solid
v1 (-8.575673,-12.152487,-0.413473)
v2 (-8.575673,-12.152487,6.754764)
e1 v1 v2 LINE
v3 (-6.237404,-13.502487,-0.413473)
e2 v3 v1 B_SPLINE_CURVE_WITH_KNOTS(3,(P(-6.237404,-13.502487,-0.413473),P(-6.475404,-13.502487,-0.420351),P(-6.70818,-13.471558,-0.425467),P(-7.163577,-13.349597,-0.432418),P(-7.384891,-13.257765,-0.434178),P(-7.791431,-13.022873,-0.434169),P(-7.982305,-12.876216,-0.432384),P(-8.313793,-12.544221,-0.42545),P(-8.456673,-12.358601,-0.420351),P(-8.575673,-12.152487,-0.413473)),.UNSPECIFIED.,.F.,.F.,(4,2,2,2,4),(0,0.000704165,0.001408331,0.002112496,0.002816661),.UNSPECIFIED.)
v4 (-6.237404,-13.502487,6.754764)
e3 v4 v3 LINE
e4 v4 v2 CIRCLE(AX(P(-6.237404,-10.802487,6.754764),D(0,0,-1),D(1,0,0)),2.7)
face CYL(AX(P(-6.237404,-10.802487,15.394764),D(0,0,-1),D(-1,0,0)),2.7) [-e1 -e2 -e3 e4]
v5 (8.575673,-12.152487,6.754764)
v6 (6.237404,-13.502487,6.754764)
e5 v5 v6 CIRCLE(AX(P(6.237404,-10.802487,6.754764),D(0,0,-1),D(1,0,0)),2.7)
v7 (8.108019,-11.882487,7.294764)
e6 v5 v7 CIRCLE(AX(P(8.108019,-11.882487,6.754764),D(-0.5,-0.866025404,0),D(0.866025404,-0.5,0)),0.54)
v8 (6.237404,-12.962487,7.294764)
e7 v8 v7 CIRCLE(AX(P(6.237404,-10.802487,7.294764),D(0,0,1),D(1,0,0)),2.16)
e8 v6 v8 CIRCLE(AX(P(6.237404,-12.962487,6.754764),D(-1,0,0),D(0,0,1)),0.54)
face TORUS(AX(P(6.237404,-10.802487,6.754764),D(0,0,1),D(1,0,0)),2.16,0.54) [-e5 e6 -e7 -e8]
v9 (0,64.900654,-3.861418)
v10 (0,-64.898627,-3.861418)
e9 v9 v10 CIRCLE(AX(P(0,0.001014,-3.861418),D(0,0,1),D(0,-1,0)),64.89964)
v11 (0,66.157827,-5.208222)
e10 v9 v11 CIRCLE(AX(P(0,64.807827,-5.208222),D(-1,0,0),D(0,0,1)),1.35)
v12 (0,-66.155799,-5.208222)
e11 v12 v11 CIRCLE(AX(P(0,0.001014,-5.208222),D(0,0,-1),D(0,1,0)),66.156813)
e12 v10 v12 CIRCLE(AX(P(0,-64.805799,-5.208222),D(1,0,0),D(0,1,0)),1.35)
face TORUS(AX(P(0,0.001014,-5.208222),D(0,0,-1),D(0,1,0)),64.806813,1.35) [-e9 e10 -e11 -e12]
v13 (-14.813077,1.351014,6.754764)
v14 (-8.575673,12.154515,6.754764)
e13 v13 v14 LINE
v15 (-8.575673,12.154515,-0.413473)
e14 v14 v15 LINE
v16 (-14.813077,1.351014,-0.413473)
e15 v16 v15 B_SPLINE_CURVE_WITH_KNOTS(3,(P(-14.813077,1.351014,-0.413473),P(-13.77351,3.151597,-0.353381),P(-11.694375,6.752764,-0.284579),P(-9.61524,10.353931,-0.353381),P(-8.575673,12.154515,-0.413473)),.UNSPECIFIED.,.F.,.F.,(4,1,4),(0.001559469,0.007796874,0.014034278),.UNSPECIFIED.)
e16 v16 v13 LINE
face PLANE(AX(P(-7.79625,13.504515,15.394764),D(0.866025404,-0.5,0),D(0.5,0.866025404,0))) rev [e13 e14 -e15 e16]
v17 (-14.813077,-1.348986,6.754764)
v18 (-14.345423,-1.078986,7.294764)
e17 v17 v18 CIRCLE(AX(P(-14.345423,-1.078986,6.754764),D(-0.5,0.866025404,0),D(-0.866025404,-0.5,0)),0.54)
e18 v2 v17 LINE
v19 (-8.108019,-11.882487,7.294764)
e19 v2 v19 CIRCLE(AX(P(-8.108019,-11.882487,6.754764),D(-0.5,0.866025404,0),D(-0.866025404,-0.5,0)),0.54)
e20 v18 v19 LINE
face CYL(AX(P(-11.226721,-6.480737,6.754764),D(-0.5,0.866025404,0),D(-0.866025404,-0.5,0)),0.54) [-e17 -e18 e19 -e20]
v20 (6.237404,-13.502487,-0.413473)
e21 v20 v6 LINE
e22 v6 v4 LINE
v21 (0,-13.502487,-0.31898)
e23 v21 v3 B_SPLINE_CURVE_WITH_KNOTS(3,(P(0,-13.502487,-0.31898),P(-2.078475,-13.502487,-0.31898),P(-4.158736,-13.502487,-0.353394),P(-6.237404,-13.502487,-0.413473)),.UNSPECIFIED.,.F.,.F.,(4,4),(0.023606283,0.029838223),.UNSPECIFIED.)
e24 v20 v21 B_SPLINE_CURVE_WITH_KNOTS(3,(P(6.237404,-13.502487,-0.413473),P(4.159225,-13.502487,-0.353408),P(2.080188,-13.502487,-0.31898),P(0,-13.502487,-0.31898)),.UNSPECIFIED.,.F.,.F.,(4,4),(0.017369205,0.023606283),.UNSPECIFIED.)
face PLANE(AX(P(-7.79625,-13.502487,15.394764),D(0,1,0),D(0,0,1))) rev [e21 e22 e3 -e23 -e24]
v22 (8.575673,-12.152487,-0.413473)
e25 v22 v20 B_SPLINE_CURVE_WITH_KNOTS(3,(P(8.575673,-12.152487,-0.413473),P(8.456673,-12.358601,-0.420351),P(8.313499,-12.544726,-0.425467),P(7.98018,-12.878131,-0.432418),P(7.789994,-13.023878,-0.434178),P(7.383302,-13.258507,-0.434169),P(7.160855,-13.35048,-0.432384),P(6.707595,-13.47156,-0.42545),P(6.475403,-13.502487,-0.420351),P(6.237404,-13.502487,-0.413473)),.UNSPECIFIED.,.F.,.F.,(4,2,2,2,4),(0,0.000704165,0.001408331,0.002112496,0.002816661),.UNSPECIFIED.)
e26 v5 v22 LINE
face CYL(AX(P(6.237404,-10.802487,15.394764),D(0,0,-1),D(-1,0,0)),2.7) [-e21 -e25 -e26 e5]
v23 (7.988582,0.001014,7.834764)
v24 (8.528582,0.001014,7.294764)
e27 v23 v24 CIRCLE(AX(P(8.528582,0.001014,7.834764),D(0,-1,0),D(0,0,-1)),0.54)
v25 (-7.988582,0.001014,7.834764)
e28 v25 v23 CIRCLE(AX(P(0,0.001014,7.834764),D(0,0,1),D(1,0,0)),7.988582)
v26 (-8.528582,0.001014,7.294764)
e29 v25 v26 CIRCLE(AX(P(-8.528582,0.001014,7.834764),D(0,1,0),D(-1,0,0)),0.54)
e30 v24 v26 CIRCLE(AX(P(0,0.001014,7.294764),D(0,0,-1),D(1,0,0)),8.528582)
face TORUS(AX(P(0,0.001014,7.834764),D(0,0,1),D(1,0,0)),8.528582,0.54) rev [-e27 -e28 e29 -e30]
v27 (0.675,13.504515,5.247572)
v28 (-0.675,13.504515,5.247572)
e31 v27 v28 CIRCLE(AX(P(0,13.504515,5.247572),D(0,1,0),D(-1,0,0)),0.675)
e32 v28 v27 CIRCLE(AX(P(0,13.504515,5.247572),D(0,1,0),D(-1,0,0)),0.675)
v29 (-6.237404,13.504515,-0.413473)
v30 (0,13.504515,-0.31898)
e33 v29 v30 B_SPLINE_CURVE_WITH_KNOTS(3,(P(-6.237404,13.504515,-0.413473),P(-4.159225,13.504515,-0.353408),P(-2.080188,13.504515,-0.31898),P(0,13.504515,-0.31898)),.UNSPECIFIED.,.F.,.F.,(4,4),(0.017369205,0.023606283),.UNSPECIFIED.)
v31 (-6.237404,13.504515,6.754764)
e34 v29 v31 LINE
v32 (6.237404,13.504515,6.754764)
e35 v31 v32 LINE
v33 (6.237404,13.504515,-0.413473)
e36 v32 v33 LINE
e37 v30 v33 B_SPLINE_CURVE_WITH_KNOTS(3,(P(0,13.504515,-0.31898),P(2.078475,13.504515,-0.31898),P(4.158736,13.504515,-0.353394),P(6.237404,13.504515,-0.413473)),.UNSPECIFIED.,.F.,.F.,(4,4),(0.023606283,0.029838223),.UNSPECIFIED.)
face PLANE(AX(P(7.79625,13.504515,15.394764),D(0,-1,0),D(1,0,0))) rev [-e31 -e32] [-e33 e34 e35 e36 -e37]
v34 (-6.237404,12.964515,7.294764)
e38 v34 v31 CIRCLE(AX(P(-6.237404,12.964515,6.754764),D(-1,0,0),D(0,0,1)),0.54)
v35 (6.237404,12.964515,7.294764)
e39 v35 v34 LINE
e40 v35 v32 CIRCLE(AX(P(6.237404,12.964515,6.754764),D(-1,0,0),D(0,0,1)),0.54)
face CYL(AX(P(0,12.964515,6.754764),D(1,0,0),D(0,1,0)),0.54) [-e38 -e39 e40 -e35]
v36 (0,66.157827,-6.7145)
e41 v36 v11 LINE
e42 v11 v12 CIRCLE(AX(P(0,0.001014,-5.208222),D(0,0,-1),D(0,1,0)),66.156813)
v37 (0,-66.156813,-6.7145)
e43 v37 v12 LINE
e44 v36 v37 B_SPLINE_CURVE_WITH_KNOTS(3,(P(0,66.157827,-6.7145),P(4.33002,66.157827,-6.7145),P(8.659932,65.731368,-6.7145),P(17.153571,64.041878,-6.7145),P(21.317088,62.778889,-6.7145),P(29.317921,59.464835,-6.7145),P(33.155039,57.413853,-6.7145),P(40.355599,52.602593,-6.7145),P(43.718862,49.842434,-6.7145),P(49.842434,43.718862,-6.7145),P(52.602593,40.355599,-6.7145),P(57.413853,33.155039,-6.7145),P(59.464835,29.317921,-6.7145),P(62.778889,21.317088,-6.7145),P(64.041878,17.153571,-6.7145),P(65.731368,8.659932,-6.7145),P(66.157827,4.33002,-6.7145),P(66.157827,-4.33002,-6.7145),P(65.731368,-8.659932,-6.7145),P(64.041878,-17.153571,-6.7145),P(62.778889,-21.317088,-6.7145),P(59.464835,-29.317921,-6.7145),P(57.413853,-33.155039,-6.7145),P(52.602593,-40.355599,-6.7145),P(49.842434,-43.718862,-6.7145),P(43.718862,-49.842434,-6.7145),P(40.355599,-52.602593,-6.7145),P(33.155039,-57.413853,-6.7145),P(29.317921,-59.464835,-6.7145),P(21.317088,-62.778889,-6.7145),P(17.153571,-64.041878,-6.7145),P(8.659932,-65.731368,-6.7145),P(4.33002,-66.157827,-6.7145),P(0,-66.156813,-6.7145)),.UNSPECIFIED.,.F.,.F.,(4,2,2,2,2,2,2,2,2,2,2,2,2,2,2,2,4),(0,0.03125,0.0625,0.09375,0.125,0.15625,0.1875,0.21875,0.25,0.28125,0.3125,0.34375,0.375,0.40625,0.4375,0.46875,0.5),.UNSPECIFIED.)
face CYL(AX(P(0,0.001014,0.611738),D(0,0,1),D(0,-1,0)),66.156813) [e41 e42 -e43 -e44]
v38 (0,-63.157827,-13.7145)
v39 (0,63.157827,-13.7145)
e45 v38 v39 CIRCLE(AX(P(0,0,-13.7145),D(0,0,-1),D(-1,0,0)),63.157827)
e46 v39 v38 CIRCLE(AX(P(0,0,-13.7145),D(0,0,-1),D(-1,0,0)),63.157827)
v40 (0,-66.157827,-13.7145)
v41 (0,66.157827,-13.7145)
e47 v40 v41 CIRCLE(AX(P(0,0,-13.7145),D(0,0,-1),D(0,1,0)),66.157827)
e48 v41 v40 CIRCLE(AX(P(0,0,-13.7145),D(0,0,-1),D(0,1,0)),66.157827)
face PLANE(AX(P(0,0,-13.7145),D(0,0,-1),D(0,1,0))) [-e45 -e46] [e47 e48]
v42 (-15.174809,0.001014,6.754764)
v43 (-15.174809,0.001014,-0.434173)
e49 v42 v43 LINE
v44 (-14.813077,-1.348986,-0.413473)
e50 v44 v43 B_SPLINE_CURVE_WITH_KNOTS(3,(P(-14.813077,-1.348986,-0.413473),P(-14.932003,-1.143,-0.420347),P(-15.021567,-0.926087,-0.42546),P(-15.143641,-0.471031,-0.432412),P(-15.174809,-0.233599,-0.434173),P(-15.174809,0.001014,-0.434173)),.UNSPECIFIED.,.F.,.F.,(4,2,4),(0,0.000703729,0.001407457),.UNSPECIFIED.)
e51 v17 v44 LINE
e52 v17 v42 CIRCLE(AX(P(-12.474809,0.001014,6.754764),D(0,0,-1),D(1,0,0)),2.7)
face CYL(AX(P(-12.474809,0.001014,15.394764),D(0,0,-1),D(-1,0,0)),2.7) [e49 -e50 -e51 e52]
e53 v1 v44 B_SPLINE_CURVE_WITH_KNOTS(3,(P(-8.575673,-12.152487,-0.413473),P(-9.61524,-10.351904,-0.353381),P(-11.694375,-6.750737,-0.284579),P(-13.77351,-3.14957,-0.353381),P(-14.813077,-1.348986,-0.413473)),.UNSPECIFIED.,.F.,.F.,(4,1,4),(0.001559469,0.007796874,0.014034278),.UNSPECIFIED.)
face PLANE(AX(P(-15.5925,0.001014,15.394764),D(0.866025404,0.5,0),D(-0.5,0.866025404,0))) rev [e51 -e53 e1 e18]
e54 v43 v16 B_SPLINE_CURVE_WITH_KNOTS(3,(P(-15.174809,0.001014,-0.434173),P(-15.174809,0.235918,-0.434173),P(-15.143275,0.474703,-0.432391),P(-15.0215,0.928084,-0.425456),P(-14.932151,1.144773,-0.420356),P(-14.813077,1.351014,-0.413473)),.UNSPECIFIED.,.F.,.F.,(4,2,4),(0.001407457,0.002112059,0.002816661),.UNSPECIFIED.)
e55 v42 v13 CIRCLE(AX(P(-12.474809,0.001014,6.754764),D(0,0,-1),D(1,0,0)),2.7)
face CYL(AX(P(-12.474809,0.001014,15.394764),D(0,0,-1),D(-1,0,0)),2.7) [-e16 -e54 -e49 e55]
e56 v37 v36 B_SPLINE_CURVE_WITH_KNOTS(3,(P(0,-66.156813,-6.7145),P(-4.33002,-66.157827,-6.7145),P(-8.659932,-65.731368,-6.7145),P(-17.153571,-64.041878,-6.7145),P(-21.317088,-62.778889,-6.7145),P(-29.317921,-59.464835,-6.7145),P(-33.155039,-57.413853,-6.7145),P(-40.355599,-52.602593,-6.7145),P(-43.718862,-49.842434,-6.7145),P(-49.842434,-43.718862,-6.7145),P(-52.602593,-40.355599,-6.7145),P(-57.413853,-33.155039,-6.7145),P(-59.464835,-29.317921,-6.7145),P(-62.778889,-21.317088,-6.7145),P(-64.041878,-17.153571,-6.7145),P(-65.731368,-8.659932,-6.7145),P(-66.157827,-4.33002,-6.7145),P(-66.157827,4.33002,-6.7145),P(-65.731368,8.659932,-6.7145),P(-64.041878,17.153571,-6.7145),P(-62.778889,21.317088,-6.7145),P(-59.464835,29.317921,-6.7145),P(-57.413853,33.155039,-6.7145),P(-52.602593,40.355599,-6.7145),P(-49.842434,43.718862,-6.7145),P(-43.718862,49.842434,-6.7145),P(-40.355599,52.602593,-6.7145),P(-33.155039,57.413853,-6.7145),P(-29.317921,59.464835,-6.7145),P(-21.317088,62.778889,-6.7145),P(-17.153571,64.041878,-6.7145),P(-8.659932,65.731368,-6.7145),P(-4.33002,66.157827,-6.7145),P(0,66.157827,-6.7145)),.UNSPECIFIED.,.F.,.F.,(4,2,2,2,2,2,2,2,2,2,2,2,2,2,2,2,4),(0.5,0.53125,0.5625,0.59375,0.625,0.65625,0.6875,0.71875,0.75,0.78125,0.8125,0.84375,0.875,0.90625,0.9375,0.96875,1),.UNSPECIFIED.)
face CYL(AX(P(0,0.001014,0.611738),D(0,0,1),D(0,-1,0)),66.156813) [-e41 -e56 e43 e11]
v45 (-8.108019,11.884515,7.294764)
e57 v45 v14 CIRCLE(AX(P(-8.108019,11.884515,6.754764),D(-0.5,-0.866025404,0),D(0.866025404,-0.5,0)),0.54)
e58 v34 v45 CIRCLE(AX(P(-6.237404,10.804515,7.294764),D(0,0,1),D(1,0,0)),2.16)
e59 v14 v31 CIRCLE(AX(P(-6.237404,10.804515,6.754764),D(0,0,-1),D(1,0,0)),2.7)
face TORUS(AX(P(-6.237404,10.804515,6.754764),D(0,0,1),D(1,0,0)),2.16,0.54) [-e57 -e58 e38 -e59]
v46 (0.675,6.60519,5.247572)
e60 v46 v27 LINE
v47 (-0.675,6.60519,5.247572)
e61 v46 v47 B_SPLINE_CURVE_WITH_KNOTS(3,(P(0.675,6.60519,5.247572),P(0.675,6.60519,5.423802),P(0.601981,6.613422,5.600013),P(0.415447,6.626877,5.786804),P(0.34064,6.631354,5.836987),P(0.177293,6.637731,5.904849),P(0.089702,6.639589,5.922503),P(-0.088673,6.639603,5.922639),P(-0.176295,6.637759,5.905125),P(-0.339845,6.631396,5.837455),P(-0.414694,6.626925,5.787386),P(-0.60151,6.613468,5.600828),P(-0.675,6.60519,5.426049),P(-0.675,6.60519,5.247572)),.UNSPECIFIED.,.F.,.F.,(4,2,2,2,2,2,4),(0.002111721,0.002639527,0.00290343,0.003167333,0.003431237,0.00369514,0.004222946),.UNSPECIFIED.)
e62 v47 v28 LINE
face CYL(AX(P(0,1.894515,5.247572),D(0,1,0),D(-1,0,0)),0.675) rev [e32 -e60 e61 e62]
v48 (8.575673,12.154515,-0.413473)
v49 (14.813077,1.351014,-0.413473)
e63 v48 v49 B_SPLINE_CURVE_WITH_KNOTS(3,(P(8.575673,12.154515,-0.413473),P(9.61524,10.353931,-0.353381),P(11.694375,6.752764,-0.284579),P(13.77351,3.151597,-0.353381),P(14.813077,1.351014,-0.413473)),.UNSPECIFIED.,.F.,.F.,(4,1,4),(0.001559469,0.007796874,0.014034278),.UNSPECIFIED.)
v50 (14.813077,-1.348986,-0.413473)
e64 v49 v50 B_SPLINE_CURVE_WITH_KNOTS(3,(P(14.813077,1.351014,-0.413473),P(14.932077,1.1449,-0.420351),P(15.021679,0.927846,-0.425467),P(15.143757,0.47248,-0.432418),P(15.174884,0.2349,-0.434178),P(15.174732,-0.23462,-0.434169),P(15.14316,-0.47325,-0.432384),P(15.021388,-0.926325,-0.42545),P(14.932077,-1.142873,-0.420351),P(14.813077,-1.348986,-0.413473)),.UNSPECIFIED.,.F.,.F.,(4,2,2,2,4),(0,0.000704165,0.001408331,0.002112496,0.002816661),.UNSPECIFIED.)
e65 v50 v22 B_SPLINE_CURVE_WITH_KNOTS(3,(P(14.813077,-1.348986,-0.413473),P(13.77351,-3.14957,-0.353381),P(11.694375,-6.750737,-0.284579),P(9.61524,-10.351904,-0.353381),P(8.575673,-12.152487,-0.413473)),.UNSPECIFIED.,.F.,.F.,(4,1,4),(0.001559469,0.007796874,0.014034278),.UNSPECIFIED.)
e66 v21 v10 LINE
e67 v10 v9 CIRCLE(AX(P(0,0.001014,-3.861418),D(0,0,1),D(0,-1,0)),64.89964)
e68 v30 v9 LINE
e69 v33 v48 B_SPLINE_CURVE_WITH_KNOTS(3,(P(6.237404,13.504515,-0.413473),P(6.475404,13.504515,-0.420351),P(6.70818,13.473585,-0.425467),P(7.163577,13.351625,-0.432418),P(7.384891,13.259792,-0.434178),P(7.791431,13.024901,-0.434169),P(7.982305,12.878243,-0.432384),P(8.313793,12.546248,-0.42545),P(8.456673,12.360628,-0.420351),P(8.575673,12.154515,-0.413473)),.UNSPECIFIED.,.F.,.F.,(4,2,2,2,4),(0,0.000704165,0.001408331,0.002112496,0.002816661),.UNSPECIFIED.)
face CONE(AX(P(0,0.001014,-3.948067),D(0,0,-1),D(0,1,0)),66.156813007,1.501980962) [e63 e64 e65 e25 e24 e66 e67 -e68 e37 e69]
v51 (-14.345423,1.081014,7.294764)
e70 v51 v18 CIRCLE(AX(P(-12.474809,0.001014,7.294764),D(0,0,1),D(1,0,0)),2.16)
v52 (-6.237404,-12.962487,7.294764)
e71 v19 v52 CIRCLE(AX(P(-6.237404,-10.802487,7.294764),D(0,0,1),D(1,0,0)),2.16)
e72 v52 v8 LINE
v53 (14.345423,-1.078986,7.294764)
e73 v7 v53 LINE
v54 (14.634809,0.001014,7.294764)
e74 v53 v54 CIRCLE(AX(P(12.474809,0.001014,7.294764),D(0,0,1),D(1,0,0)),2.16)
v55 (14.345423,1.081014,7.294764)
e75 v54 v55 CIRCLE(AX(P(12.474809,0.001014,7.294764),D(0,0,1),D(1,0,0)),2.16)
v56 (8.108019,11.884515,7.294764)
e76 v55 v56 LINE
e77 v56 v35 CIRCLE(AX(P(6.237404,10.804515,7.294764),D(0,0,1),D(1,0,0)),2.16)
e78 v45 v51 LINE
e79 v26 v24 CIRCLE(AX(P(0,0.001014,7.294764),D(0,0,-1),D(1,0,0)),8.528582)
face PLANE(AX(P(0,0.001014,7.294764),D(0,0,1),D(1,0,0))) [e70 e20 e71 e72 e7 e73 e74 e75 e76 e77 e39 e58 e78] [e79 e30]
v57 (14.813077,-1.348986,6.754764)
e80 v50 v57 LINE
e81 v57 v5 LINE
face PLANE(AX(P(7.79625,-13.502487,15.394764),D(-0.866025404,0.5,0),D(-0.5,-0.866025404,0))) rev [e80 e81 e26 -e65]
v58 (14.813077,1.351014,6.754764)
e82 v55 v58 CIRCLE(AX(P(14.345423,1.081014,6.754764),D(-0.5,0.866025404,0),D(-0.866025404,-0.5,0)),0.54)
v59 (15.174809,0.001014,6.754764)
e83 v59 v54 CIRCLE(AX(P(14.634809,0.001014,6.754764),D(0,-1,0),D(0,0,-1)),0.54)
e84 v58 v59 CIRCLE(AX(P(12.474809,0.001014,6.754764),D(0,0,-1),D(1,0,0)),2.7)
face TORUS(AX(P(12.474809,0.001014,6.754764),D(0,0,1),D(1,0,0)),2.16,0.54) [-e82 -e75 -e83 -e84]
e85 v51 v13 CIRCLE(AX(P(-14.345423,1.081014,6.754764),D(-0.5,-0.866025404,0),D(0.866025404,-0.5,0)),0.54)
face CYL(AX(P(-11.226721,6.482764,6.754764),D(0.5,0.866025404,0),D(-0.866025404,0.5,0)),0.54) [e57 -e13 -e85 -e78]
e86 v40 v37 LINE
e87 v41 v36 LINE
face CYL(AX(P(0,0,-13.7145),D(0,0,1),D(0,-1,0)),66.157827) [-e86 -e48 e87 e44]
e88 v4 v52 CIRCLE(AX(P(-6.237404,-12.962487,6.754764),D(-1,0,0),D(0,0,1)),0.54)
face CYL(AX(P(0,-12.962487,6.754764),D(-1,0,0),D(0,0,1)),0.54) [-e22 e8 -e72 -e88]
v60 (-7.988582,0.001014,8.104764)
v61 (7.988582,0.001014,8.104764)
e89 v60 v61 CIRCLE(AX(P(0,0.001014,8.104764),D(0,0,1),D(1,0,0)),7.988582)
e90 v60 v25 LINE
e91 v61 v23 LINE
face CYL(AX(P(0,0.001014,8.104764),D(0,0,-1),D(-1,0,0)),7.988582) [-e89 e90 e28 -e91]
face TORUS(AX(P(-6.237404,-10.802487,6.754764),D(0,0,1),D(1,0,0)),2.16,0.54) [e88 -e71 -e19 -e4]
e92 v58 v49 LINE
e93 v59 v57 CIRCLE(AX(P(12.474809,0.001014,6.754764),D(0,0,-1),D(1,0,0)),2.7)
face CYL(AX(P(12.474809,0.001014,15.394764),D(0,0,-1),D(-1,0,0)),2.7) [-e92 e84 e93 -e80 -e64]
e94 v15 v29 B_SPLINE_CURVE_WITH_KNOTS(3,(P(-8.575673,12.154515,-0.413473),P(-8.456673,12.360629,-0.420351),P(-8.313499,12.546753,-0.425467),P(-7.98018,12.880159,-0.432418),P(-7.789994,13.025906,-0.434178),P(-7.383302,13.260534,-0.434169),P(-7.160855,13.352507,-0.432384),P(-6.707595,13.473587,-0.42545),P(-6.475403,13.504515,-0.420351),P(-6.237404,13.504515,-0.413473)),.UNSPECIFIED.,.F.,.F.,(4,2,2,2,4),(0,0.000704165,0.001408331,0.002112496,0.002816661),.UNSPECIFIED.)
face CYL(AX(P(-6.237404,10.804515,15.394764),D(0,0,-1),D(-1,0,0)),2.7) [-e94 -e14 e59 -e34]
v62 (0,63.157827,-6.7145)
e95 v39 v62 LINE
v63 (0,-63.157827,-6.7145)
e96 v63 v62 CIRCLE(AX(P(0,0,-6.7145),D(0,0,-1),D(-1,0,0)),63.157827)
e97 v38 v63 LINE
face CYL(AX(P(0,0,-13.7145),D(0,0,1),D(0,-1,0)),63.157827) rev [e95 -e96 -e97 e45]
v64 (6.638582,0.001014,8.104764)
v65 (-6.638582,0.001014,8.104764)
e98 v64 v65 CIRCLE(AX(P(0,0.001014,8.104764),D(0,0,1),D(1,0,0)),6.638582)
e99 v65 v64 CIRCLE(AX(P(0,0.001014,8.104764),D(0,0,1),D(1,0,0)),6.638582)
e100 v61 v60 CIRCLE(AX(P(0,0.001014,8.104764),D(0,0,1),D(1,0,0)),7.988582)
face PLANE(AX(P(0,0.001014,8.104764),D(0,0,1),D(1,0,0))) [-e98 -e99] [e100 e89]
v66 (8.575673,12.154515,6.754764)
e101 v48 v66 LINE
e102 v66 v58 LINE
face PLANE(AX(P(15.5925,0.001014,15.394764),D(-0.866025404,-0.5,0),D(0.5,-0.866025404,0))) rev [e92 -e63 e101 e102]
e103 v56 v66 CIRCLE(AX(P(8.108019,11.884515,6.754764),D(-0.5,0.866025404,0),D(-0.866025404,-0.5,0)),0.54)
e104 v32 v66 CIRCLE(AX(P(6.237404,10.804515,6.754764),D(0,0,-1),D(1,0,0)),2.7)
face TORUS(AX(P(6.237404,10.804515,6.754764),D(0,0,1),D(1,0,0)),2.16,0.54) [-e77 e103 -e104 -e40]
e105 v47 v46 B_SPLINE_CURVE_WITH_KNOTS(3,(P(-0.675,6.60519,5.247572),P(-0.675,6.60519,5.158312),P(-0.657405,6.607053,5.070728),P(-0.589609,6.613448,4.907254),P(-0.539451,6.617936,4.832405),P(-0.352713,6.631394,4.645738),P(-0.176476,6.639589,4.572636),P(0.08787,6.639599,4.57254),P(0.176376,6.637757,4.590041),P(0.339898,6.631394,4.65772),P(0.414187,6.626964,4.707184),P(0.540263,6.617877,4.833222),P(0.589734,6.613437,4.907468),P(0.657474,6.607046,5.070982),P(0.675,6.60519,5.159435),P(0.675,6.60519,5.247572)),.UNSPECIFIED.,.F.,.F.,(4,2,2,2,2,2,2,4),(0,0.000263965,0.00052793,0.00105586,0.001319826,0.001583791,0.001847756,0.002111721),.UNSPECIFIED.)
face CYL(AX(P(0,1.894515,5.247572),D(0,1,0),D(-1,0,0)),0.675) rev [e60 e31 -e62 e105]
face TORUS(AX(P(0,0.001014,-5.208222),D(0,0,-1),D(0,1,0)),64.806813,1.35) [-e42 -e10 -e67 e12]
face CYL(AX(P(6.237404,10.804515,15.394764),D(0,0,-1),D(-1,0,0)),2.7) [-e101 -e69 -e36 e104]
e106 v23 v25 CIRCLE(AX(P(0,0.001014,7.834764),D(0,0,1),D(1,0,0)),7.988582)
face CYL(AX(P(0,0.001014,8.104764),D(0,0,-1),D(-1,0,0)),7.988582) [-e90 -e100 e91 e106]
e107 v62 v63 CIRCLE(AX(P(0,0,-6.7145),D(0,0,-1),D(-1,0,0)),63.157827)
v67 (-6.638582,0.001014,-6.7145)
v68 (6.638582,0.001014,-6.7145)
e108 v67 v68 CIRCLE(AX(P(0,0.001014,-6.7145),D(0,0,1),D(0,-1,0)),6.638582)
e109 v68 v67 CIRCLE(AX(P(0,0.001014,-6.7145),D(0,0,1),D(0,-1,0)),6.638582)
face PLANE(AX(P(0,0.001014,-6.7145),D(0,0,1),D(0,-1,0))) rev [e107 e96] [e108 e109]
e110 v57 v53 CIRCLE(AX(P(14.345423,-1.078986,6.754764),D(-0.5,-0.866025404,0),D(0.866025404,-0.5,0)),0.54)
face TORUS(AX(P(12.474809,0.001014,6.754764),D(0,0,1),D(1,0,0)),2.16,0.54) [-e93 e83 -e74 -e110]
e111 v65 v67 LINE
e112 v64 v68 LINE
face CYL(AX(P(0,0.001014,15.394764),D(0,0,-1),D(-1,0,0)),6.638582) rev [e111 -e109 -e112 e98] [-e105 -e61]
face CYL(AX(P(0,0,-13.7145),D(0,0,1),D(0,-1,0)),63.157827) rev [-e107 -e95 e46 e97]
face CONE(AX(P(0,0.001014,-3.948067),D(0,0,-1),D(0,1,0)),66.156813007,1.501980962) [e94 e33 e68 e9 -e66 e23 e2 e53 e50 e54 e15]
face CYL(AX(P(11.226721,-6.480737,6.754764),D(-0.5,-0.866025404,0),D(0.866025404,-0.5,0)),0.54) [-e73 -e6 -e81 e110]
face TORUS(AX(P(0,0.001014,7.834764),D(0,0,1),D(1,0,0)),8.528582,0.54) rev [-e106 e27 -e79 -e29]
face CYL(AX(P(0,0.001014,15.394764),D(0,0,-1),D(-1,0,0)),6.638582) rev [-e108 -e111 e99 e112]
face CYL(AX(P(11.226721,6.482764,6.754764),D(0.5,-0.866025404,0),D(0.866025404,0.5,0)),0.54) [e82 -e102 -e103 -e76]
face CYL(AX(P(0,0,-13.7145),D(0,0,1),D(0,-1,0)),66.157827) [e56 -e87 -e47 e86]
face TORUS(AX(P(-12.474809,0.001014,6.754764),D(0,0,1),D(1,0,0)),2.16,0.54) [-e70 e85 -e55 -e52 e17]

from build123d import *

# Parameters (mm, degrees)
SKETCH1_R           = 2.458734123
BOSS_EXTRUDE_DEPTH  = 3.2
CUT_EXTRUDE1_DEPTH  = 3
FILLET1_R           = 0.5
FILLET2_R           = 1
SKETCH7_R           = 2.958734123
SKETCH7_R_2         = 2.458734123
EXTRUDE_THIN1_DEPTH = 0.3
FILLET3_R           = 0.2
SKETCH8_R           = 0.25
CUT_EXTRUDE2_DEPTH  = 4.3
CUT_EXTRUDE3_START  = -14.3
SKETCH9_R           = 2.458734123
CUT_EXTRUDE3_DEPTH  = 14.3
SCALE1_SCALE        = 2.7
SKETCH10_R          = 66.157826775
SKETCH10_R_2        = 63.157826775
EXTRUDE_THIN2_DEPTH = 7


with BuildPart() as part:
    # Sketch1 → Boss-Extrude (new, symmetric)
    with BuildSketch(Plane.XY):
        Polygon((2.8875, 5.001296707), (-2.8875, 5.001296707), (-5.775, 0), (-2.8875, -5.001296707), (2.8875, -5.001296707), (5.775, 0), align=None)
        Circle(SKETCH1_R, mode=Mode.SUBTRACT)
    extrude(amount=BOSS_EXTRUDE_DEPTH, both=True)

    # Sketch5 → Revolve1 (revolve)
    with BuildSketch(Plane(origin=(0, 0, 0), x_dir=(0, 0, -1), z_dir=(1, 0, 0))):
        Polygon((2.275194756, 0), (3.964011499, 24.502523336), (4.988616082, 24.502523336), (4.988616082, 0), align=None)
    revolve(axis=Axis((0, 0, -2.275194756), (0, 0, -1)))

    # Sketch6 → Cut-Extrude1 (cut)
    with BuildSketch(Plane.XY.offset(3.2)):
        Polygon((5.775, 0), (2.8875, 5.001296707), (-2.8875, 5.001296707), (-5.775, 0), (-2.8875, -5.001296707), (2.8875, -5.001296707), align=None)
    extrude(amount=-CUT_EXTRUDE1_DEPTH, mode=Mode.SUBTRACT)

    # Fillet1
    fillet1_edges = [part.edges().sort_by_distance(p)[0] for p in [
        (0, -24.502523336, -3.964011499),
    ]]
    fillet(fillet1_edges, radius=FILLET1_R)

    # Fillet2
    fillet2_edges = [part.edges().sort_by_distance(p)[0] for p in [
        (-2.8875, -5.001296707, -1.236615997),
        (2.8875, -5.001296707, -1.236615997),
        (5.775, 0, -1.236615997),
        (-2.8875, 5.001296707, -1.236615997),
        (-5.775, 0, -1.236615997),
        (2.8875, 5.001296707, -1.236615997),
    ]]
    fillet(fillet2_edges, radius=FILLET2_R)

    # Sketch7 → Extrude-Thin1 (add)
    with BuildSketch(Plane.XY.offset(0.2)):
        Circle(SKETCH7_R)
        Circle(SKETCH7_R_2, mode=Mode.SUBTRACT)
    extrude(amount=EXTRUDE_THIN1_DEPTH)

    # Fillet3
    fillet3_edges = [part.edges().sort_by_distance(p)[0] for p in [
        (-2.958734123, 0, 0.2),
        (0, -5.001296707, 0.2),
        (-4.33125, -2.500648353, 0.2),
        (4.33125, -2.500648353, 0.2),
        (4.33125, 2.500648353, 0.2),
        (0, 5.001296707, 0.2),
        (-4.33125, 2.500648353, 0.2),
        (2.810149731, 4.867322111, 0.2),
        (-5.620299462, 0, 0.2),
        (-2.810149731, 4.867322111, 0.2),
        (5.620299462, 0, 0.2),
        (2.810149731, -4.867322111, 0.2),
        (-2.810149731, -4.867322111, 0.2),
    ]]
    fillet(fillet3_edges, radius=FILLET3_R)

    # Sketch8 → Cut-Extrude2 (cut)
    with BuildSketch(Plane(origin=(0, 5.001296707, 0), x_dir=(1, 0, 0), z_dir=(0, 1, 0))):
        with Locations(Location((0, 0.558219382, 0), (0, 0, 180))):
            Circle(SKETCH8_R)
    extrude(amount=-CUT_EXTRUDE2_DEPTH, mode=Mode.SUBTRACT)

    # Sketch9 → Cut-Extrude3 (cut)
    with BuildSketch(Plane.XY.offset(CUT_EXTRUDE3_START)):
        with Locations(Location((0, 0, 0), (0, 0, 270))):
            Circle(SKETCH9_R)
    extrude(amount=CUT_EXTRUDE3_DEPTH, mode=Mode.SUBTRACT)


with BuildPart() as part_1:
    # Scale1: scaled about (1.23e-07, -0.000596522, -3.973390116)
    add(part.part.scale(SCALE1_SCALE).moved(Location((-2.09e-07, 0.001014087, 6.754763197))))

    # Sketch10 → Extrude-Thin2 (add)
    with BuildSketch(Plane(origin=(0, 0, -6.714499546), x_dir=(-1, 0, 0), z_dir=(0, 0, -1))):
        Circle(SKETCH10_R)
        Circle(SKETCH10_R_2, mode=Mode.SUBTRACT)
    extrude(amount=EXTRUDE_THIN2_DEPTH)


solid = part_1.part
